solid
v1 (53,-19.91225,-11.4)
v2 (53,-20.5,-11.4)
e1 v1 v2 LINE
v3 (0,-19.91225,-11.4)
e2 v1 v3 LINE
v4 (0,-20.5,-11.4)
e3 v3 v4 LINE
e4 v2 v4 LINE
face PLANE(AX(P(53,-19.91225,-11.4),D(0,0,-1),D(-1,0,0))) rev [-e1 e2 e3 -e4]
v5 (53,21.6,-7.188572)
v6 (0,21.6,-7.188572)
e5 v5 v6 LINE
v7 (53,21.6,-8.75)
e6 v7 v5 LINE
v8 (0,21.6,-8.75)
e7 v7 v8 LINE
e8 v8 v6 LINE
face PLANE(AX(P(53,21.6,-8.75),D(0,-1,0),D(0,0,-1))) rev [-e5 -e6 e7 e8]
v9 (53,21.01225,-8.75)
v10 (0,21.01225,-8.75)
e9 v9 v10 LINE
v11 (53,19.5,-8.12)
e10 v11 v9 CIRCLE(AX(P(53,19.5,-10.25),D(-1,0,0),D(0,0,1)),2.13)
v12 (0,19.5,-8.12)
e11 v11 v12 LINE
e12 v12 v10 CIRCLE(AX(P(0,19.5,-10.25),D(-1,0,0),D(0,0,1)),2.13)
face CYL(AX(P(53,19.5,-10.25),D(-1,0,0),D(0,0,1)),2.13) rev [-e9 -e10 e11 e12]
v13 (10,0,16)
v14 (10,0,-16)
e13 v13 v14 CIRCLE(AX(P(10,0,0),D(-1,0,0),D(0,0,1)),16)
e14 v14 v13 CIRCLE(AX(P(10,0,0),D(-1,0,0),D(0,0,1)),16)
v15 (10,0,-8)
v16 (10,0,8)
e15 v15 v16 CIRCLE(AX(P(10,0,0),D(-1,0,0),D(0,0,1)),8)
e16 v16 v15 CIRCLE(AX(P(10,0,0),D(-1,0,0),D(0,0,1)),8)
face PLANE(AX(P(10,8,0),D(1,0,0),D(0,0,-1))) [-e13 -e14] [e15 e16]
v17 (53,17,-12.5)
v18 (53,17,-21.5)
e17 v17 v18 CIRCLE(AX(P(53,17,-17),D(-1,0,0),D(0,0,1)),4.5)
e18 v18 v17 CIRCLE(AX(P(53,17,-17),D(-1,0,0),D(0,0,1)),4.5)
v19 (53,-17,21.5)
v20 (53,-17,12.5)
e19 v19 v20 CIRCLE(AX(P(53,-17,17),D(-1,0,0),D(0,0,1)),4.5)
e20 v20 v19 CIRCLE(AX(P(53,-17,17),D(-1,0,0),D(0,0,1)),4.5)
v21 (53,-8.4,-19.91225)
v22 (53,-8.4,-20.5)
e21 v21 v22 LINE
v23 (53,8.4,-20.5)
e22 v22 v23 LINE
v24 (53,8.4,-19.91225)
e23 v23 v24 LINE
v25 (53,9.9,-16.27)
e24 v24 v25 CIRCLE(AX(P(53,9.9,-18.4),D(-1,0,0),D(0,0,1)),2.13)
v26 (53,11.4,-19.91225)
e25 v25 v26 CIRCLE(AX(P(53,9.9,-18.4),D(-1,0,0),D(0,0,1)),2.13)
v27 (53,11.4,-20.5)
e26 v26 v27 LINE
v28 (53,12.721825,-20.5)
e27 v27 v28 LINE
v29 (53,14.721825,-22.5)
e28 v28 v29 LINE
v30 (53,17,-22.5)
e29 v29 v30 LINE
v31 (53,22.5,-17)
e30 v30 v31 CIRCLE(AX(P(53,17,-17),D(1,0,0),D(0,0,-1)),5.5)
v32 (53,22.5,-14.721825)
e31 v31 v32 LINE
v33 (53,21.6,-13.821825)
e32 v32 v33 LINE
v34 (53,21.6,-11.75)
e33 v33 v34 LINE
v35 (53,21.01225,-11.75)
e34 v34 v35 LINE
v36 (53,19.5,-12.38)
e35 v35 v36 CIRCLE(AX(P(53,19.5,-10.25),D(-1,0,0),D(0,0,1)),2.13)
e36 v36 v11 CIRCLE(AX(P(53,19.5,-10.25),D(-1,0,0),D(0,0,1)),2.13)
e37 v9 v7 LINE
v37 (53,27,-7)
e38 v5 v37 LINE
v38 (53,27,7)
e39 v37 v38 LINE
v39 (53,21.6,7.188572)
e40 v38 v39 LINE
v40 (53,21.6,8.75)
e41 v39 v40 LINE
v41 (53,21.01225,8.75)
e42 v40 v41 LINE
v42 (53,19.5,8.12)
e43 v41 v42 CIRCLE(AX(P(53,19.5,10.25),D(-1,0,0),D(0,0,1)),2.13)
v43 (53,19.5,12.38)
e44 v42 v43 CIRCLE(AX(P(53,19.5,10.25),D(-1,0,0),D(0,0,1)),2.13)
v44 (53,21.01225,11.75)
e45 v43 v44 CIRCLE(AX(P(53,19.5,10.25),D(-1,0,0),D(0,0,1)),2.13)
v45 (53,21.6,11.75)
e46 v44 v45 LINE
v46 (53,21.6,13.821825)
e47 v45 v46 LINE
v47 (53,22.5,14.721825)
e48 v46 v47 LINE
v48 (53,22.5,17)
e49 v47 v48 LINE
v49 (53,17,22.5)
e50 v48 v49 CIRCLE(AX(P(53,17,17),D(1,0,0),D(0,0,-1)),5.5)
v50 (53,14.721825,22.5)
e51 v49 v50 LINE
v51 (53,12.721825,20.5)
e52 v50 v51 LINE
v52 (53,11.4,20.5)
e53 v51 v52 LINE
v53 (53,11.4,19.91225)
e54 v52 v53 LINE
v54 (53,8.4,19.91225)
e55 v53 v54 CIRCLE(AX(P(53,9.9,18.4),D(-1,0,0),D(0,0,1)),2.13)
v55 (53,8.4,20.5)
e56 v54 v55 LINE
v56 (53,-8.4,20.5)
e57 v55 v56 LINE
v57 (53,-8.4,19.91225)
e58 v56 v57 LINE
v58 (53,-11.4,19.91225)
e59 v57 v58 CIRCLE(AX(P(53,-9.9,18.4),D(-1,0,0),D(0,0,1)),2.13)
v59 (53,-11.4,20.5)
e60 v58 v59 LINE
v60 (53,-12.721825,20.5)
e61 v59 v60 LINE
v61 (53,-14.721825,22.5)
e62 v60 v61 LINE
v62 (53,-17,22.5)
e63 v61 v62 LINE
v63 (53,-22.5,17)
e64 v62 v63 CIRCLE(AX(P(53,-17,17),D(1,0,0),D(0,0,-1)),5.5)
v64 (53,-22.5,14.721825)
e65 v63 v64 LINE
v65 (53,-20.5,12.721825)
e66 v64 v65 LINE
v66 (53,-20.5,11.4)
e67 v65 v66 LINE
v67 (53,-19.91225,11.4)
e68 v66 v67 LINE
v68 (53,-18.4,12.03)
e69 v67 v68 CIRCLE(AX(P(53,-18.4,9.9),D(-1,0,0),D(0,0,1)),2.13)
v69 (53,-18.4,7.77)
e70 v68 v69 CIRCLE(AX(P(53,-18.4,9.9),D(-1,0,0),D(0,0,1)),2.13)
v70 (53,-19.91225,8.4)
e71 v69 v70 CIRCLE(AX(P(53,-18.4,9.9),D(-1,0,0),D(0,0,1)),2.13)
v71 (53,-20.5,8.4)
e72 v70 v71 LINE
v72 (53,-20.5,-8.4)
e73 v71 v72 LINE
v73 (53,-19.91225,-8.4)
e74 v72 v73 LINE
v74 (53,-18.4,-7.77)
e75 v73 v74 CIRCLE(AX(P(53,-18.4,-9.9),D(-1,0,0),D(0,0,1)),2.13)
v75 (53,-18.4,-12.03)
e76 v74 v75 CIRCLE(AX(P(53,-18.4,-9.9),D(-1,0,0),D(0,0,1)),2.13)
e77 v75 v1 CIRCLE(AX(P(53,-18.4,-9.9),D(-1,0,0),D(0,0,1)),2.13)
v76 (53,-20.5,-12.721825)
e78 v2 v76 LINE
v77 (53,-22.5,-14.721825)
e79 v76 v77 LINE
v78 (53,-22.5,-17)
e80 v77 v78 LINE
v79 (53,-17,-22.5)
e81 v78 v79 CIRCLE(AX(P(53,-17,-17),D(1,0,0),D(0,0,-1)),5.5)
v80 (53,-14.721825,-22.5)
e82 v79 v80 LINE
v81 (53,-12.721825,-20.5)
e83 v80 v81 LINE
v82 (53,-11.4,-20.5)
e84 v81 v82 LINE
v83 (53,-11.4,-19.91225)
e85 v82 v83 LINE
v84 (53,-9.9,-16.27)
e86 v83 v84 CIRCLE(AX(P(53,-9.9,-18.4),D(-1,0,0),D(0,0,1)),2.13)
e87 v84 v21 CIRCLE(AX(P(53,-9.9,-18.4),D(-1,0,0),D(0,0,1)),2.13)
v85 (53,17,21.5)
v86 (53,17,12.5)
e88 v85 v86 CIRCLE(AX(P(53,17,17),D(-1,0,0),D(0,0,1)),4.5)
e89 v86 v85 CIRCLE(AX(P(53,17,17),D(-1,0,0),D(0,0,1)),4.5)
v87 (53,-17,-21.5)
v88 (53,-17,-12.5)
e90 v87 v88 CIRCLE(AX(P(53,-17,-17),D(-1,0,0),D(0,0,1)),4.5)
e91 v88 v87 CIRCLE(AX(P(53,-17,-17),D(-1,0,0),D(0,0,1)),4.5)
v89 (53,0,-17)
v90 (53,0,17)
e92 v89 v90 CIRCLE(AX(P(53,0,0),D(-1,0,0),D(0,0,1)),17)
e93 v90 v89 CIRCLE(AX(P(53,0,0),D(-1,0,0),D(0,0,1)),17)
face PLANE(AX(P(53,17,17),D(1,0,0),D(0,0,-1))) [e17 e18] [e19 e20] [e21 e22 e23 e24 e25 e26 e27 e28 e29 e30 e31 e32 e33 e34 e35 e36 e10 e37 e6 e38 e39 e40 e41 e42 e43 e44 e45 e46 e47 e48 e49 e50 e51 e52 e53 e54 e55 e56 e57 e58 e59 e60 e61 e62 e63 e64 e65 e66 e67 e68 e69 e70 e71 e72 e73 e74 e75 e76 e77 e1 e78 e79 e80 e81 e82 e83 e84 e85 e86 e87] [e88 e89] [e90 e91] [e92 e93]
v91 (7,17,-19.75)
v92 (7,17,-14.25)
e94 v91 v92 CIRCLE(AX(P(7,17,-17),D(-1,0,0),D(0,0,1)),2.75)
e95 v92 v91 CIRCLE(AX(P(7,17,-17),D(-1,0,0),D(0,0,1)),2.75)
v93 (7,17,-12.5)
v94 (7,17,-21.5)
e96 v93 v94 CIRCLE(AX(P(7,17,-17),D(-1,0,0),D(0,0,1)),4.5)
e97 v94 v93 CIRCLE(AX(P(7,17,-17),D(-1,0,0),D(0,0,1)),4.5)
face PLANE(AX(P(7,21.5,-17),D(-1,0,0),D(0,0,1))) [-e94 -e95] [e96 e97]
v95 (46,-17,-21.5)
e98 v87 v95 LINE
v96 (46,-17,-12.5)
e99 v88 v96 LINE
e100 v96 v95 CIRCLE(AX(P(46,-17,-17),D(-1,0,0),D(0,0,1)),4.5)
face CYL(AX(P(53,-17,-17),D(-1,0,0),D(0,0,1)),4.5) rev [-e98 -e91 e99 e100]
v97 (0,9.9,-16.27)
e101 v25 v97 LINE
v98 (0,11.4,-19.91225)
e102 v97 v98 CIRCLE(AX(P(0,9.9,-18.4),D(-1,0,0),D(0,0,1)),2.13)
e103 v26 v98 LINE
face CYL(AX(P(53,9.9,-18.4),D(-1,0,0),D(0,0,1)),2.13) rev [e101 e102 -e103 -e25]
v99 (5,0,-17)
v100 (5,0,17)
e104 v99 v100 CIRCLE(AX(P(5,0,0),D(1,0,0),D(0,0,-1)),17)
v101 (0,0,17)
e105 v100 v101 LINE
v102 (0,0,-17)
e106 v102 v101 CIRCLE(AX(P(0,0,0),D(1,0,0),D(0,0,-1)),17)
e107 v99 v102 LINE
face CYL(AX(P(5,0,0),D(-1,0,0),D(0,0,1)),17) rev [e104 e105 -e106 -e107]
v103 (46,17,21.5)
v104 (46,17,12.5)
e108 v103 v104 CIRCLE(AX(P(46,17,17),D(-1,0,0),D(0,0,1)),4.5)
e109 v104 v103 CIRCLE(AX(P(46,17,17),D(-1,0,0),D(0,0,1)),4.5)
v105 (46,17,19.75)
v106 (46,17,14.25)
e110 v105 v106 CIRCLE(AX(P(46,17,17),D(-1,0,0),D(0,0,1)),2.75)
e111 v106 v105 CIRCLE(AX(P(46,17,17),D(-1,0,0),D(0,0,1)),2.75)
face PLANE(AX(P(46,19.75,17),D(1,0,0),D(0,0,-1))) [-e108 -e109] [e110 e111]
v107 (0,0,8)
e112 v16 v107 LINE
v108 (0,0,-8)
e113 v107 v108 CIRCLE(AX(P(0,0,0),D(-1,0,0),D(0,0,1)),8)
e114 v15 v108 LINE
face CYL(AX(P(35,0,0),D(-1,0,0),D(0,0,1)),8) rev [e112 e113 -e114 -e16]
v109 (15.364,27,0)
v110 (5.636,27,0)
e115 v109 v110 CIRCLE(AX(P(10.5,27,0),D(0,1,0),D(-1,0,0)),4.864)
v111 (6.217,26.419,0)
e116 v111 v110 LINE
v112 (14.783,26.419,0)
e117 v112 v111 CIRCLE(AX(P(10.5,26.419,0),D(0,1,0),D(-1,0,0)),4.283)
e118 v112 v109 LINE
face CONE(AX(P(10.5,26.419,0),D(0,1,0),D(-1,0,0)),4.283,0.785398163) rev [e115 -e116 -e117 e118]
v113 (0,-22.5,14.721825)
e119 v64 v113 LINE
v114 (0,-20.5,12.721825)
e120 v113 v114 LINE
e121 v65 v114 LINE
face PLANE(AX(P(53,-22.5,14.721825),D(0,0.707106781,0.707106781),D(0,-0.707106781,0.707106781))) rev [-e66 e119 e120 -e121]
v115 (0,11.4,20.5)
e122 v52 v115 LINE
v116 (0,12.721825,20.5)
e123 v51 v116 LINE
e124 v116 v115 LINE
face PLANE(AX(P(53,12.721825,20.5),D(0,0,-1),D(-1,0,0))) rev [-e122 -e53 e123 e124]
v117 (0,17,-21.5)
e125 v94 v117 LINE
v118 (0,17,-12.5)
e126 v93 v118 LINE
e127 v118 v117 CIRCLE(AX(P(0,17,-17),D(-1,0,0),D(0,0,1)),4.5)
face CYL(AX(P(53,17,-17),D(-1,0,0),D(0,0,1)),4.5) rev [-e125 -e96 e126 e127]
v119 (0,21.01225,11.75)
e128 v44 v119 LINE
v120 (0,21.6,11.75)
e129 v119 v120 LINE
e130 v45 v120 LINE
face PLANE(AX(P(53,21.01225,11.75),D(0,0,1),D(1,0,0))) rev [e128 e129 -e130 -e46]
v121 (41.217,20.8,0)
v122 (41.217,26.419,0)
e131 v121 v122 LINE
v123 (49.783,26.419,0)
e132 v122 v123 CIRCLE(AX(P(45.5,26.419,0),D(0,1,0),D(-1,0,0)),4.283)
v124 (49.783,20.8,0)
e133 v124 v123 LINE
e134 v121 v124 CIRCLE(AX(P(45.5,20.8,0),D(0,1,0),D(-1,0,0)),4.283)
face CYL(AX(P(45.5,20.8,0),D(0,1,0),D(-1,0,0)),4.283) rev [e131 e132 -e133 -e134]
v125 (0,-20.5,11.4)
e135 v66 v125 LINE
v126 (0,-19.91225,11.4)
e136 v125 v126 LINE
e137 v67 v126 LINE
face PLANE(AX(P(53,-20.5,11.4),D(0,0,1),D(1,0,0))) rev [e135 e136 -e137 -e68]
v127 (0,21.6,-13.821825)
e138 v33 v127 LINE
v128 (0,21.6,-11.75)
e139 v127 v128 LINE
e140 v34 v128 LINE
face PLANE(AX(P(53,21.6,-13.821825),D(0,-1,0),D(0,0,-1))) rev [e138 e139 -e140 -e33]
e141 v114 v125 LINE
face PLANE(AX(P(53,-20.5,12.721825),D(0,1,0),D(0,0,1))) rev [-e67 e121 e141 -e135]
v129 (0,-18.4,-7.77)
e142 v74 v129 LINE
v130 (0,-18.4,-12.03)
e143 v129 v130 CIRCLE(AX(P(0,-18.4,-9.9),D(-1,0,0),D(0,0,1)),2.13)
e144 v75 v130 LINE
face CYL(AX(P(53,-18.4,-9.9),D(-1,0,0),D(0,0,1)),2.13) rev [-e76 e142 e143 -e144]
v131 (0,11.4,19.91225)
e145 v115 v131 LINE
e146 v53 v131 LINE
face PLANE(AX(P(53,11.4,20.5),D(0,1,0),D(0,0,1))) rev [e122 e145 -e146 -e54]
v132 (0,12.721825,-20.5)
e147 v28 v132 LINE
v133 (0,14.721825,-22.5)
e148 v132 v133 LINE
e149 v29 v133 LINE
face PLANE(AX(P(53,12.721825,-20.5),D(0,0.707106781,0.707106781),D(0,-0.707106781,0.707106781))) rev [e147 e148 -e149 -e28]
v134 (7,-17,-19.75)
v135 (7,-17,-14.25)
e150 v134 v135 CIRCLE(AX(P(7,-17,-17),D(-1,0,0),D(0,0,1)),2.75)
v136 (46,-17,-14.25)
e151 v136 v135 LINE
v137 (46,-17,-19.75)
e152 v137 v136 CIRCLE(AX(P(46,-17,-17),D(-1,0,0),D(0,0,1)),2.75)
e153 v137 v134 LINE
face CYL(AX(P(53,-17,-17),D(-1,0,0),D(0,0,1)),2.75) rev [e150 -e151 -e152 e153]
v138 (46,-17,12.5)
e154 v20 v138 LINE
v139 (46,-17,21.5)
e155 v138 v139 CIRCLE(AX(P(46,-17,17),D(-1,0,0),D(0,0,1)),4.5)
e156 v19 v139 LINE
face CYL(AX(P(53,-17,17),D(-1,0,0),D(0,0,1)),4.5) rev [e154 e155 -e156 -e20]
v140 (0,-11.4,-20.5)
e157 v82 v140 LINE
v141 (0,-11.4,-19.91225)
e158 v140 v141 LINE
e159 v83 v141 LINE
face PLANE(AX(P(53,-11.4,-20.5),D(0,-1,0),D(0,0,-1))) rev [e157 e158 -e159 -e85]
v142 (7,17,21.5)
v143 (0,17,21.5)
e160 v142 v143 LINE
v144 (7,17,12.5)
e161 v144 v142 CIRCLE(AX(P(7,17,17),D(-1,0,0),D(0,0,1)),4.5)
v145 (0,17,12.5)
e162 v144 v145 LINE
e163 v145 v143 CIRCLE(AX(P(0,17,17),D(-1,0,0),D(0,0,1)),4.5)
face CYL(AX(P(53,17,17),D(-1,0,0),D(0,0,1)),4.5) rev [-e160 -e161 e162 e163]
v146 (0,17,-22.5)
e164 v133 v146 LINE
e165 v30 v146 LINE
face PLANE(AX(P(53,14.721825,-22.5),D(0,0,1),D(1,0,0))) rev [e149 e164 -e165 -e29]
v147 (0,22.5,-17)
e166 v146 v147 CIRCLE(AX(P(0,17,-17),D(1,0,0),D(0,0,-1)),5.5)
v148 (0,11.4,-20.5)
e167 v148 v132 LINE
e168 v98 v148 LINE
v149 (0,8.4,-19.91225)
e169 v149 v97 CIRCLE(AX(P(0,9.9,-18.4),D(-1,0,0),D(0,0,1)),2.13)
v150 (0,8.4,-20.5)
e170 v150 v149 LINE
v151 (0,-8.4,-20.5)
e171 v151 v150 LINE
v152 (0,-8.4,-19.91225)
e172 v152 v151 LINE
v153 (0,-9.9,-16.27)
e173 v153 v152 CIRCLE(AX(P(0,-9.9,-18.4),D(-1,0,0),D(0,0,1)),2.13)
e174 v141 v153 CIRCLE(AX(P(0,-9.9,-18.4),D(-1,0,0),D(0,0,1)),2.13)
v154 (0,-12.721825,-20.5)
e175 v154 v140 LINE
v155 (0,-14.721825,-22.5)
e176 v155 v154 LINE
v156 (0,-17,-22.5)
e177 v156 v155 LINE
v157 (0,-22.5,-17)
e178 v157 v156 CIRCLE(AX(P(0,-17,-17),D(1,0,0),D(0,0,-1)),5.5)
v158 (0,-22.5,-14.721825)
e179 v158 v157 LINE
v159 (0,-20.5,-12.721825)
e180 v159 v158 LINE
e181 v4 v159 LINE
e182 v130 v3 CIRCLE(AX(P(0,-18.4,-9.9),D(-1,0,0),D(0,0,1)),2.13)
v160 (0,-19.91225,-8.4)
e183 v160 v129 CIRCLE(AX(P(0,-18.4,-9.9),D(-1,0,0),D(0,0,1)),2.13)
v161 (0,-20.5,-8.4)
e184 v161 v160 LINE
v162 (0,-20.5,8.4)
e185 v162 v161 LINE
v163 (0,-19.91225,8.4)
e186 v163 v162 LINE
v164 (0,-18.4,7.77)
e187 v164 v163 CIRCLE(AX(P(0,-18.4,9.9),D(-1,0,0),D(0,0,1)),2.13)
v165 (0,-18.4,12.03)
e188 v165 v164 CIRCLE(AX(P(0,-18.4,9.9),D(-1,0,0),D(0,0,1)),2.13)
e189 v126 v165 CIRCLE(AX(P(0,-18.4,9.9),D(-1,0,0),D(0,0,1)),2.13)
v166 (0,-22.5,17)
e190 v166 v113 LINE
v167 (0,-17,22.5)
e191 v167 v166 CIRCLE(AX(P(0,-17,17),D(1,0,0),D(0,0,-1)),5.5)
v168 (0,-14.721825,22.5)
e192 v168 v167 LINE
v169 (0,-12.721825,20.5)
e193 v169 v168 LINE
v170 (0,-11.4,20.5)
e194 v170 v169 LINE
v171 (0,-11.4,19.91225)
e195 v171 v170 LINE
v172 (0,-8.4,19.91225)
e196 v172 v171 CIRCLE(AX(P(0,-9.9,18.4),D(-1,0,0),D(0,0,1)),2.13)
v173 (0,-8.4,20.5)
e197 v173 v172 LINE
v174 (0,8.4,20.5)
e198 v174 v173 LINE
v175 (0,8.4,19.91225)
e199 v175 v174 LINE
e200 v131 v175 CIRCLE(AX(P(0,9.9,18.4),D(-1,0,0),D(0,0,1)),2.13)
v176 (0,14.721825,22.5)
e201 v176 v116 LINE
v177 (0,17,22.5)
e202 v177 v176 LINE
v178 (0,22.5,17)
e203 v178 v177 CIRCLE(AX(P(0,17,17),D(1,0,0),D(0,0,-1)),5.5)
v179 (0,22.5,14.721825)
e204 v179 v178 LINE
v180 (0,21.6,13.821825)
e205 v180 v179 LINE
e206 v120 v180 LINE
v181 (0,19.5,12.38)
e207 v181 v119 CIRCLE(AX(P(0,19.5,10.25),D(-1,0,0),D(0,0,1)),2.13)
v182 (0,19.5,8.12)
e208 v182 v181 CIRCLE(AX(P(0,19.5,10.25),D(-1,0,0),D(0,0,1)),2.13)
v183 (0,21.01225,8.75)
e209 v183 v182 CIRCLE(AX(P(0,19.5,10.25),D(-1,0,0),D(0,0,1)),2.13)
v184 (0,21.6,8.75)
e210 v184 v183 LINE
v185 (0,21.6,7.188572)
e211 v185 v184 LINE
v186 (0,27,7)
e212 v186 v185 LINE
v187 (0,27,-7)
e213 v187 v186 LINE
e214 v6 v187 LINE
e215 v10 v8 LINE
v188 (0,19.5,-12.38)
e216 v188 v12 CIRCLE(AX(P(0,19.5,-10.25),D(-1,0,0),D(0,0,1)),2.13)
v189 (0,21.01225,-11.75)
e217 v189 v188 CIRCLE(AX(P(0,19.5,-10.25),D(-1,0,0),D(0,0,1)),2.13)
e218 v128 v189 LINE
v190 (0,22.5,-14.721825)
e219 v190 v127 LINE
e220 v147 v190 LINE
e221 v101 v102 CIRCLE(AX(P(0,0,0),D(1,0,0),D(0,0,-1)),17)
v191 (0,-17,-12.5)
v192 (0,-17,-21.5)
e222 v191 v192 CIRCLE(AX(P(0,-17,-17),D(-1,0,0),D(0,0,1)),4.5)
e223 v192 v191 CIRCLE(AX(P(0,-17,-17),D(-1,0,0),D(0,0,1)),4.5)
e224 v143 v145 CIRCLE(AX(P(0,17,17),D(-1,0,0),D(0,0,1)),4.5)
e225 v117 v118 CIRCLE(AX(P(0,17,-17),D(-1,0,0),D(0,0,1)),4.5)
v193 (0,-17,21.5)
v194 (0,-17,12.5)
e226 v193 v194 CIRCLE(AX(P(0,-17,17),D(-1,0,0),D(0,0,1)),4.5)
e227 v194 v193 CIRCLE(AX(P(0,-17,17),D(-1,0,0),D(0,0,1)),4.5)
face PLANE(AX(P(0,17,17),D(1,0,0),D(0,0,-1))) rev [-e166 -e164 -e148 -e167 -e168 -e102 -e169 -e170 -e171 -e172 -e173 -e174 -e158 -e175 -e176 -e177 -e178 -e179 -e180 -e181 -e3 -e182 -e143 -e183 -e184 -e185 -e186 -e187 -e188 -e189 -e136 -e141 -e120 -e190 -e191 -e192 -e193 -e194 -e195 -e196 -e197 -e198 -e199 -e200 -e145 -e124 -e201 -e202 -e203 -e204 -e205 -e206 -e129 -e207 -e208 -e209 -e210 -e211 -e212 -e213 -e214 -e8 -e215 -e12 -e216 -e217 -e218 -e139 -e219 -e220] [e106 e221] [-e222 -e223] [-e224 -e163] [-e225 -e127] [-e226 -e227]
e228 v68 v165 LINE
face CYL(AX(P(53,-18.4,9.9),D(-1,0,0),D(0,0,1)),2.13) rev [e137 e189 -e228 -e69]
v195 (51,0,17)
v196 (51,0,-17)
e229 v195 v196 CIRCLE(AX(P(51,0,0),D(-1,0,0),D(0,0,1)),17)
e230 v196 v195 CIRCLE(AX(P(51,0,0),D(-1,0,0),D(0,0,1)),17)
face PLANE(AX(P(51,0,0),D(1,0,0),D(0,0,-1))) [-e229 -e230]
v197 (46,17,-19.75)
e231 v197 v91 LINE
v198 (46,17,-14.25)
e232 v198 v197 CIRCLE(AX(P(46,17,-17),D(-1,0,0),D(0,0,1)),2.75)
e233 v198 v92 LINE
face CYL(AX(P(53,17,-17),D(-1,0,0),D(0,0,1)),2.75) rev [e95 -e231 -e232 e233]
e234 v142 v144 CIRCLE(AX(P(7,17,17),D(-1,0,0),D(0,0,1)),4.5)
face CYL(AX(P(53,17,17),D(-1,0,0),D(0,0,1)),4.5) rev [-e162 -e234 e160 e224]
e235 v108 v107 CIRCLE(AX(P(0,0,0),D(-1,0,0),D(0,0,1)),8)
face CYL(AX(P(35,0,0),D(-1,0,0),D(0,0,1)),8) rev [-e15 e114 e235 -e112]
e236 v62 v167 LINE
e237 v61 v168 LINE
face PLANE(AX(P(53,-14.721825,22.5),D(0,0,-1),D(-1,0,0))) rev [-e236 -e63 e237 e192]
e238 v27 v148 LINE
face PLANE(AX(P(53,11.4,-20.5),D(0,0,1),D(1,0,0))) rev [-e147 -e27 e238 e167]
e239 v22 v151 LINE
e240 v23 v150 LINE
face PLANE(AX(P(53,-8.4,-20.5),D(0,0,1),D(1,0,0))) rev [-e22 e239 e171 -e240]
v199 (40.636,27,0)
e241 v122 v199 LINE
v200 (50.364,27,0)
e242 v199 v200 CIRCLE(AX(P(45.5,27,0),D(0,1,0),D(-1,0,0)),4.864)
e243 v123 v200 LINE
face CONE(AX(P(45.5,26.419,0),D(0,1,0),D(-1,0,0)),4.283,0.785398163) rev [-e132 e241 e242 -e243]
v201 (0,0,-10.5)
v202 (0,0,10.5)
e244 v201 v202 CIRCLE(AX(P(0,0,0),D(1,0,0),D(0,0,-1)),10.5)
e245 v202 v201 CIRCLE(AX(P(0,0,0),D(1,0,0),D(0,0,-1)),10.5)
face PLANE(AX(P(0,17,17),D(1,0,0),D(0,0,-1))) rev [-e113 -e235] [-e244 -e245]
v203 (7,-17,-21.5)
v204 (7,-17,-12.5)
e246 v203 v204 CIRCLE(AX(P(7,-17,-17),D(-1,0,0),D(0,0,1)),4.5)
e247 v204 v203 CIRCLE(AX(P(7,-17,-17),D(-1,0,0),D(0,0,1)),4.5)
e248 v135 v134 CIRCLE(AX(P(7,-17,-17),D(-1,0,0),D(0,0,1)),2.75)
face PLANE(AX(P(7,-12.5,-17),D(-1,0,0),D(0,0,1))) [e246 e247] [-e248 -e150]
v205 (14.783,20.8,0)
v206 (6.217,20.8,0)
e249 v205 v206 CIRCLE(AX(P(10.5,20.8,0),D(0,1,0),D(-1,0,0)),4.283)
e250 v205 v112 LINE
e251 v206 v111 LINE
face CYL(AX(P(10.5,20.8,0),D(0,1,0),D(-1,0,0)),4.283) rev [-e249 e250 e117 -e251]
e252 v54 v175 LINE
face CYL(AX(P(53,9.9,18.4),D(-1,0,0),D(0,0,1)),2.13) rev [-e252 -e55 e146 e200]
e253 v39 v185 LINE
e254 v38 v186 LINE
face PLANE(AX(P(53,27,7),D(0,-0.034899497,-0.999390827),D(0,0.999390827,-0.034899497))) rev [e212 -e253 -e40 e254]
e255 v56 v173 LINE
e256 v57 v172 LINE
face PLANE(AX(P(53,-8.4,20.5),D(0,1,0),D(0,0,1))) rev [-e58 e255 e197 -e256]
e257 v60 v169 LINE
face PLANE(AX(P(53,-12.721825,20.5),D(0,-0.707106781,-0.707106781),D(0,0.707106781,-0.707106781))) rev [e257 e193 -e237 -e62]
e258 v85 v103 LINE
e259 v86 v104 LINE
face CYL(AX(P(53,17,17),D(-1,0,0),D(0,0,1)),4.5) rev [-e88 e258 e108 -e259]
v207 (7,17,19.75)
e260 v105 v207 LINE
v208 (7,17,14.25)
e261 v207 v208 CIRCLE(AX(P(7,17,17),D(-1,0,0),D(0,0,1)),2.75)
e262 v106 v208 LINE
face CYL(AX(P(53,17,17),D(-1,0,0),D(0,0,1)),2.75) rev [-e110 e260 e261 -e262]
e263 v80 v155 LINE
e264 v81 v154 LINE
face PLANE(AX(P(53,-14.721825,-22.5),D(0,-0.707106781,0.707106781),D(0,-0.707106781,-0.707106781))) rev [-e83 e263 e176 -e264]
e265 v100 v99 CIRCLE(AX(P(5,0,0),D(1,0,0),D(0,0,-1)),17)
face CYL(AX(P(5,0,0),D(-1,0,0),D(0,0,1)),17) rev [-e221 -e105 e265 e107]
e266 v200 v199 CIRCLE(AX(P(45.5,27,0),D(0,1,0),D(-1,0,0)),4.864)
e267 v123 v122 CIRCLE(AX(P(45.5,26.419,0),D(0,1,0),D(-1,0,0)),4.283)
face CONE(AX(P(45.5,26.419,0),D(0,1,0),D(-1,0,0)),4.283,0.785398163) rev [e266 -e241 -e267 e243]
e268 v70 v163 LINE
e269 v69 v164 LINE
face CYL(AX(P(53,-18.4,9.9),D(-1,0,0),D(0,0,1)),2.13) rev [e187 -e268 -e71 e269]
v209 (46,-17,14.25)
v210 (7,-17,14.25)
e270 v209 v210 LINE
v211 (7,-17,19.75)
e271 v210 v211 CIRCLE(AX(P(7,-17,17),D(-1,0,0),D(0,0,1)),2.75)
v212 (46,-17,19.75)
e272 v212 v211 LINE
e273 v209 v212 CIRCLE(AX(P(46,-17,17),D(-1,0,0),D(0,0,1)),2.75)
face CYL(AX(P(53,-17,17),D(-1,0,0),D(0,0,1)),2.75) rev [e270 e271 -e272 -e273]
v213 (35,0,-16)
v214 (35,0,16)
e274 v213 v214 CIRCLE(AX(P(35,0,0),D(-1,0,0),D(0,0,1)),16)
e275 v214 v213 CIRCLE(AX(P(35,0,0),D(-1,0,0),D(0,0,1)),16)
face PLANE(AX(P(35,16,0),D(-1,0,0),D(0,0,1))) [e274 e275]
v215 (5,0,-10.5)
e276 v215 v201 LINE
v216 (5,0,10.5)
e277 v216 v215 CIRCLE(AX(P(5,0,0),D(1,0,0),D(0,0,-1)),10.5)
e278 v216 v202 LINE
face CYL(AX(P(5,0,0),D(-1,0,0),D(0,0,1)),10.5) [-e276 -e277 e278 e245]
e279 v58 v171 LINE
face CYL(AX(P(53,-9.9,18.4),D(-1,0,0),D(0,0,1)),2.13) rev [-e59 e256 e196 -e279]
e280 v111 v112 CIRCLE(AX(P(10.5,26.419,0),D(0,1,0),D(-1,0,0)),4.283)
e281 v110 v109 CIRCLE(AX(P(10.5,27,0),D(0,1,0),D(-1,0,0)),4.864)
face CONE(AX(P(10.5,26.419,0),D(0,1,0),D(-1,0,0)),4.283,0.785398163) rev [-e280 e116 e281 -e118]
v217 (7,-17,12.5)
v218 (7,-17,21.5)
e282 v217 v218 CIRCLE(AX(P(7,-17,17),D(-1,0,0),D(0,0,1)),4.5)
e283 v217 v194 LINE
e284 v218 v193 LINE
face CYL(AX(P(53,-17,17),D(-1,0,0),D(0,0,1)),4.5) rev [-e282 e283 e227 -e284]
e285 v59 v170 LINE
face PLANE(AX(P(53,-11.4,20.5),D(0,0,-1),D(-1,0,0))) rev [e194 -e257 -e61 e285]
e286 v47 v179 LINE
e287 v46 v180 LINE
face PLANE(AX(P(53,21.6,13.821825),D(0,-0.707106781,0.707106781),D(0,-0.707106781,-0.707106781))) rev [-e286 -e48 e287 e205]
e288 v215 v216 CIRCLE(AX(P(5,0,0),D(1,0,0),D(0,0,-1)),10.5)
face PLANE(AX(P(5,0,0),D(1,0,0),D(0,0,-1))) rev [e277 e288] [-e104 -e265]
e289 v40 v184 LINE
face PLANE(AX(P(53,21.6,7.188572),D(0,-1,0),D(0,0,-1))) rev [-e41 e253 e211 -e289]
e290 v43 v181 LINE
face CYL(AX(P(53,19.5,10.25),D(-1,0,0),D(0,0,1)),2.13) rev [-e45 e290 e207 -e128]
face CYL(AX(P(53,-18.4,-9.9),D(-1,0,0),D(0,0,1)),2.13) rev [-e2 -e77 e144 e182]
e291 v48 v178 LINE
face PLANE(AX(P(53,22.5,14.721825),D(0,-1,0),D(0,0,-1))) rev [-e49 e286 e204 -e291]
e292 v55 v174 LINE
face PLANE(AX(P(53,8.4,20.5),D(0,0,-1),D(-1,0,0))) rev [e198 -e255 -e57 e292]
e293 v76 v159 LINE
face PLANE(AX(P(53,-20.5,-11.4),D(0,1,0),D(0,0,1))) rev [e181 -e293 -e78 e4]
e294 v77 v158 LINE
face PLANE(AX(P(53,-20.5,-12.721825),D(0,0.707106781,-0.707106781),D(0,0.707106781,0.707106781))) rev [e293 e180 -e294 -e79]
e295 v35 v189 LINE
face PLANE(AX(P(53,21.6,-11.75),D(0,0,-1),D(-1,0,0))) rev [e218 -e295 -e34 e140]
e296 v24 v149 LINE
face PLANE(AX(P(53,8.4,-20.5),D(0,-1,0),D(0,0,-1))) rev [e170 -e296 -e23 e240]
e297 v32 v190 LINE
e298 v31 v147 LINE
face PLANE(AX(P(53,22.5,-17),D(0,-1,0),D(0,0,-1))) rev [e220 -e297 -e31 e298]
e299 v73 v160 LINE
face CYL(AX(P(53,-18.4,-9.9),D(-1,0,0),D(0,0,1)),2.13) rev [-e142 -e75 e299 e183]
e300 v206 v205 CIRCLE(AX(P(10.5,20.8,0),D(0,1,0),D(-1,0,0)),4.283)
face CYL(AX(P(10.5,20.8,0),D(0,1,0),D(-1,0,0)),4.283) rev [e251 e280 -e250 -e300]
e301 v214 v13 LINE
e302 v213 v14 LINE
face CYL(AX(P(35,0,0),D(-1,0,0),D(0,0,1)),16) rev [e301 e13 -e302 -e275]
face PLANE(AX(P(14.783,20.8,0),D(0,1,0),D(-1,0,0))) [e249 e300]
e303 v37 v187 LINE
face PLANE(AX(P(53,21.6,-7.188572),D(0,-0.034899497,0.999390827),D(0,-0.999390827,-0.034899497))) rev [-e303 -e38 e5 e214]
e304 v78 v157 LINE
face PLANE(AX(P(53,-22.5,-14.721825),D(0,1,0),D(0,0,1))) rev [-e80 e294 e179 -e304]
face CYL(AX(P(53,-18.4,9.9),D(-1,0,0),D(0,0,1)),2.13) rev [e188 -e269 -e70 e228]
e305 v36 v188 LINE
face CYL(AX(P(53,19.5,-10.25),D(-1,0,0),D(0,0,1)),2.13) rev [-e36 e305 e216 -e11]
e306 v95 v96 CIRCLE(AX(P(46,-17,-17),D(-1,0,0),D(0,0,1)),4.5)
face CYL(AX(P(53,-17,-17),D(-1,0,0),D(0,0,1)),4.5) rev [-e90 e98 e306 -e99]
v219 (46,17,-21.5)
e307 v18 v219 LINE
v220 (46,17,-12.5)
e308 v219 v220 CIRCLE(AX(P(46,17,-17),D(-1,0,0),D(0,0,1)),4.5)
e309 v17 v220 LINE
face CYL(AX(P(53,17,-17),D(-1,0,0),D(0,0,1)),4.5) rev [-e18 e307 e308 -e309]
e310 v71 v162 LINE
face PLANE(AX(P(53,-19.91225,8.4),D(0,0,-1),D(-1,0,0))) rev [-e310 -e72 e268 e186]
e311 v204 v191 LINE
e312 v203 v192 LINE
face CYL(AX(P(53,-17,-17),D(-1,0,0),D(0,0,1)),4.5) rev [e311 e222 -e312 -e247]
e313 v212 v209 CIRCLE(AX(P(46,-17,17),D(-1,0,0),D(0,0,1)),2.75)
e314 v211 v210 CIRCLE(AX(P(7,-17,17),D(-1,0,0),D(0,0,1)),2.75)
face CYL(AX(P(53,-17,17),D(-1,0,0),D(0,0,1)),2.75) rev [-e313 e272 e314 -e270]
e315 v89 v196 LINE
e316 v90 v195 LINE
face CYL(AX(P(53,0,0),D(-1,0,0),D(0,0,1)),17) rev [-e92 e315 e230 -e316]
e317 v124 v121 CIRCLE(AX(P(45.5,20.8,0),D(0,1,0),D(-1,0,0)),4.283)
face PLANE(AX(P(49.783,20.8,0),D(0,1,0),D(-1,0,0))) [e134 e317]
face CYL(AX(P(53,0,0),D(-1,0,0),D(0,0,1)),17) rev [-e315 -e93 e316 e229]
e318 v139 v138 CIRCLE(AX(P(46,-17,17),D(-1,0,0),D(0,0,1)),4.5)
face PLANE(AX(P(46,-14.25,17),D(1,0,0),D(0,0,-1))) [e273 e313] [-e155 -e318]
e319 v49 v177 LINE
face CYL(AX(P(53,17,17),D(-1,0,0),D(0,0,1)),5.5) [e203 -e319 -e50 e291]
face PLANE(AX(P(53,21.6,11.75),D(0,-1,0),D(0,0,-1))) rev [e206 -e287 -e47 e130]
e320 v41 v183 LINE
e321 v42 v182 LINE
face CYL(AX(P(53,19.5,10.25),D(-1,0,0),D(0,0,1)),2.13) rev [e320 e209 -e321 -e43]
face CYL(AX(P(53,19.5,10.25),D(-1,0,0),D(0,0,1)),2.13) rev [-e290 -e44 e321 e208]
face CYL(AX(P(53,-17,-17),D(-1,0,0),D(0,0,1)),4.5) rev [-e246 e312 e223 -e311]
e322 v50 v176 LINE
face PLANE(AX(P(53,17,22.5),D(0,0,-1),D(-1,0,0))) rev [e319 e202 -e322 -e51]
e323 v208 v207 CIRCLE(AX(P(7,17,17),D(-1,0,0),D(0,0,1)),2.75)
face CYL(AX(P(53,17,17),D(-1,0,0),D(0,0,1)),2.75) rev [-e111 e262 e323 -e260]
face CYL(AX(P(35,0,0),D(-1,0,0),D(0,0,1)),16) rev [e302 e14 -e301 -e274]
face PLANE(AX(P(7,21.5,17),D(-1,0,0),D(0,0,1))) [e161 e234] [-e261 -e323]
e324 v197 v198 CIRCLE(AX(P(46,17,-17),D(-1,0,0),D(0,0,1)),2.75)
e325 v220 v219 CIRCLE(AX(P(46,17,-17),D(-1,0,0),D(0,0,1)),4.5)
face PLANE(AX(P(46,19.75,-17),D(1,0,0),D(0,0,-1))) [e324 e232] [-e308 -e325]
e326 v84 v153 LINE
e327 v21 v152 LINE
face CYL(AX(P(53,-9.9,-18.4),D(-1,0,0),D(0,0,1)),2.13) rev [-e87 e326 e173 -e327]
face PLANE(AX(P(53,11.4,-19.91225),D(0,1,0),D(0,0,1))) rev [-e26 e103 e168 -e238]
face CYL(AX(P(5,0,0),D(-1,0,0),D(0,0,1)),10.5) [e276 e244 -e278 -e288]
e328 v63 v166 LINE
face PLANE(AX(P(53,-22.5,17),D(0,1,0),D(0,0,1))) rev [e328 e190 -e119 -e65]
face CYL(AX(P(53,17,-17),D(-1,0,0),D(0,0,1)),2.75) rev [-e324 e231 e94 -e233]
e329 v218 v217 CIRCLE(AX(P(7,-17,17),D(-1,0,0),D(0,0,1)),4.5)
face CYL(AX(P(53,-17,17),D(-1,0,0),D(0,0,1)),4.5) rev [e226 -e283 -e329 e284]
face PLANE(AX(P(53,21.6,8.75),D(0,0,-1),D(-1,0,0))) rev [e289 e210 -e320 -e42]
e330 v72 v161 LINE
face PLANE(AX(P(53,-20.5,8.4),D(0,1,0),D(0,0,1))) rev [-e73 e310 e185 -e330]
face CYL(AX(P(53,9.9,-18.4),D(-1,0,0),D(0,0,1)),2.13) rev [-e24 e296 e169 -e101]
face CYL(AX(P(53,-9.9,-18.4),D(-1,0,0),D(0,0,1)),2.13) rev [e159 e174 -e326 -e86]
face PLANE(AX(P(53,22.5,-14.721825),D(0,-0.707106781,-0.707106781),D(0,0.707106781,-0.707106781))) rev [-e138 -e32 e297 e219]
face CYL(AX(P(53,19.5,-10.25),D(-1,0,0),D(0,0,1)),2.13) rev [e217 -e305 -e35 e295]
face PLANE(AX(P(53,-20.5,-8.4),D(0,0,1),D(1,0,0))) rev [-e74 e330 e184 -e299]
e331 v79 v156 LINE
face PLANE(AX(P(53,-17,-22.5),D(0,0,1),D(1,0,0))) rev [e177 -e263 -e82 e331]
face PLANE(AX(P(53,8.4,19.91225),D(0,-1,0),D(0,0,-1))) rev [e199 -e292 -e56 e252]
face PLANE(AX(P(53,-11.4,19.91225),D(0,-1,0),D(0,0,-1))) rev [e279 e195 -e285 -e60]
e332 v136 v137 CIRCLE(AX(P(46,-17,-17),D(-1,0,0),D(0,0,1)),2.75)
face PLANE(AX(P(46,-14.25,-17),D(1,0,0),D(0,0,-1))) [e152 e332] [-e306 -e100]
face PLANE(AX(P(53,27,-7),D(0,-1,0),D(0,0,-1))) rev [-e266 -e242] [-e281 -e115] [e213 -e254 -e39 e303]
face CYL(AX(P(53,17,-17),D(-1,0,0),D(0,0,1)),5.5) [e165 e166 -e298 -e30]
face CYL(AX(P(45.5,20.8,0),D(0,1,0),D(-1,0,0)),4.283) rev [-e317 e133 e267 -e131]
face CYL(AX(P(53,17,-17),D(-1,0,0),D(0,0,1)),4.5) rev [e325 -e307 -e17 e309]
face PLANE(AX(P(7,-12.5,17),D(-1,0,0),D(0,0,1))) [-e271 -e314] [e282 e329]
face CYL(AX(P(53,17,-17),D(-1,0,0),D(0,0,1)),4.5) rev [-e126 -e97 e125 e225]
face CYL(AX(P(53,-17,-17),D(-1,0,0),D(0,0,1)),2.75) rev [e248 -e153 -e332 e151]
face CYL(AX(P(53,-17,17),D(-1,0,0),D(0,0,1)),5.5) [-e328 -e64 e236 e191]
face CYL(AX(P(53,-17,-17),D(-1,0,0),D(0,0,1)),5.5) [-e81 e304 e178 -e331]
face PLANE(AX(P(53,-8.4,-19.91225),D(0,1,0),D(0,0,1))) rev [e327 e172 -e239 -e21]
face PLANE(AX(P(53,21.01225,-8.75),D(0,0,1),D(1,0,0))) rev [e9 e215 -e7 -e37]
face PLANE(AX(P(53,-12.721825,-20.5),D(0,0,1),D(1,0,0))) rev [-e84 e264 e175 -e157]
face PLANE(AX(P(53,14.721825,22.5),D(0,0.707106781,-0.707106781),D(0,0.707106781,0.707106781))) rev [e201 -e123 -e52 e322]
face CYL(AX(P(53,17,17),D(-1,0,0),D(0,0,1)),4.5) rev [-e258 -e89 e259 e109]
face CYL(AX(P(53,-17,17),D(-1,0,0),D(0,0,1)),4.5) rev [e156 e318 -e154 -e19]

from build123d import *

# Parameters (mm, degrees)
BOSS_EXTRUDE1_DEPTH  = 53
SKETCH2_W            = 2
SKETCH2_H            = 17
CUT_EXTRUDE1_START   = 5
SKETCH3_R            = 17
SKETCH3_R_2          = 10.5
CUT_EXTRUDE1_DEPTH   = 5
LPATTERN1_COUNT      = 2
LPATTERN1_PITCH      = 34
LPATTERN1_COUNT_DIR2 = 2
LPATTERN1_PITCH_DIR2 = 34


with BuildPart() as part:
    # Sketch1 → Boss-Extrude1 (new body)
    with BuildSketch(Plane(origin=(0, 0, 0), x_dir=(0, 0, -1), z_dir=(1, 0, 0))):
        with BuildLine():
            Line((-22.5, 17), (-22.5, 14.721825407))
            Line((-22.5, 14.721825407), (-20.5, 12.721825407))
            Line((-20.5, 12.721825407), (-20.5, 11.4))
            Line((-20.5, 11.4), (-19.912249979, 11.4))
            ThreePointArc((-19.912249979, 11.4), (-16.27, 9.9), (-19.912249979, 8.4))
            Line((-19.912249979, 8.4), (-20.5, 8.4))
            Line((-20.5, 8.4), (-20.5, -8.4))
            Line((-20.5, -8.4), (-19.912249979, -8.4))
            ThreePointArc((-19.912249979, -8.4), (-16.27, -9.9), (-19.912249979, -11.4))
            Line((-19.912249979, -11.4), (-20.5, -11.4))
            Line((-20.5, -11.4), (-20.5, -12.721825407))
            Line((-20.5, -12.721825407), (-22.5, -14.721825407))
            Line((-22.5, -14.721825407), (-22.5, -17))
            ThreePointArc((-22.5, -17), (-20.889087297, -20.889087297), (-17, -22.5))
            Line((-17, -22.5), (-14.721825407, -22.5))
            Line((-14.721825407, -22.5), (-12.721825407, -20.5))
            Line((-12.721825407, -20.5), (-11.4, -20.5))
            Line((-11.4, -20.5), (-11.4, -19.912249979))
            ThreePointArc((-11.4, -19.912249979), (-9.9, -16.27), (-8.4, -19.912249979))
            Line((-8.4, -19.912249979), (-8.4, -20.5))
            Line((-8.4, -20.5), (8.4, -20.5))
            Line((8.4, -20.5), (8.4, -19.912249979))
            ThreePointArc((8.4, -19.912249979), (9.9, -16.27), (11.4, -19.912249979))
            Line((11.4, -19.912249979), (11.4, -20.5))
            Line((11.4, -20.5), (12.721825407, -20.5))
            Line((12.721825407, -20.5), (14.721825407, -22.5))
            Line((14.721825407, -22.5), (17, -22.5))
            ThreePointArc((17, -22.5), (20.889087297, -20.889087297), (22.5, -17))
            Line((22.5, -17), (22.5, -14.721825407))
            Line((22.5, -14.721825407), (20.5, -12.721825407))
            Line((20.5, -12.721825407), (20.5, -11.4))
            Line((20.5, -11.4), (19.912249979, -11.4))
            ThreePointArc((19.912249979, -11.4), (16.27, -9.9), (19.912249979, -8.4))
            Line((19.912249979, -8.4), (20.5, -8.4))
            Line((20.5, -8.4), (20.5, 8.4))
            Line((20.5, 8.4), (19.912249979, 8.4))
            ThreePointArc((19.912249979, 8.4), (16.27, 9.9), (19.912249979, 11.4))
            Line((19.912249979, 11.4), (20.5, 11.4))
            Line((20.5, 11.4), (20.5, 12.721825407))
            Line((20.5, 12.721825407), (22.5, 14.721825407))
            Line((22.5, 14.721825407), (22.5, 17))
            ThreePointArc((22.5, 17), (20.889087297, 20.889087297), (17, 22.5))
            Line((17, 22.5), (14.721825407, 22.5))
            Line((14.721825407, 22.5), (13.821825407, 21.6))
            Line((13.821825407, 21.6), (11.75, 21.6))
            Line((11.75, 21.6), (11.75, 21.012249979))
            ThreePointArc((11.75, 21.012249979), (10.25, 17.37), (8.75, 21.012249979))
            Line((8.75, 21.012249979), (8.75, 21.6))
            Line((8.75, 21.6), (7.188572155, 21.6))
            Line((7.188572155, 21.6), (7, 27))
            Line((7, 27), (-7, 27))
            Line((-7, 27), (-7.188572155, 21.6))
            Line((-7.188572155, 21.6), (-8.75, 21.6))
            Line((-8.75, 21.6), (-8.75, 21.012249979))
            ThreePointArc((-8.75, 21.012249979), (-10.25, 17.37), (-11.75, 21.012249979))
            Line((-11.75, 21.012249979), (-11.75, 21.6))
            Line((-11.75, 21.6), (-13.821825407, 21.6))
            Line((-13.821825407, 21.6), (-14.721825407, 22.5))
            Line((-14.721825407, 22.5), (-17, 22.5))
            ThreePointArc((-17, 22.5), (-20.889087297, 20.889087297), (-22.5, 17))
        make_face()
    extrude(amount=BOSS_EXTRUDE1_DEPTH)

    # Sketch2 → Cut-Revolve1 (revolve, cut)
    with BuildSketch(Plane.XY, mode=Mode.PRIVATE) as cut_revolve1_sk:
        with Locations((52, 8.5)):
            Rectangle(SKETCH2_W, SKETCH2_H)
    revolve(cut_revolve1_sk.sketch.rotate(Axis((53, 0, 0), (-1, 0, 0)), 270), axis=Axis((53, 0, 0), (-1, 0, 0)), mode=Mode.SUBTRACT)

    # Sketch3 → Cut-Extrude1 (cut)
    with BuildSketch(Plane(origin=(0, 0, 0), x_dir=(0, 0, -1), z_dir=(1, 0, 0)).offset(CUT_EXTRUDE1_START)):
        with Locations(Location((0, 0, 0), (0, 0, 180))):
            Circle(SKETCH3_R)
        Circle(SKETCH3_R_2, mode=Mode.SUBTRACT)
    extrude(amount=-CUT_EXTRUDE1_DEPTH, mode=Mode.SUBTRACT)

    # Sketch4 → Cut-Revolve2 (revolve, cut)
    with BuildSketch(Plane.XY, mode=Mode.PRIVATE) as cut_revolve2_sk:
        Polygon((0, 0), (0, 8), (10, 8), (10, 16), (35, 16), (35, 0), align=None)
    revolve(cut_revolve2_sk.sketch.rotate(Axis((35, 0, 0), (-1, 0, 0)), 270), axis=Axis((35, 0, 0), (-1, 0, 0)), mode=Mode.SUBTRACT)

    # Sketch5 → Cut-Revolve3 (revolve, cut)
    with BuildSketch(Plane.XY, mode=Mode.PRIVATE) as cut_revolve3_sk:
        Polygon((10.5, 27), (15.364, 27), (14.783, 26.419), (14.783, 20.8), (10.5, 20.8), align=None)
    revolve(cut_revolve3_sk.sketch.rotate(Axis((10.5, 20.8, 0), (0, 1, 0)), 180), axis=Axis((10.5, 20.8, 0), (0, 1, 0)), mode=Mode.SUBTRACT)

    # Sketch6 → Cut-Revolve4 (revolve, cut)
    with BuildSketch(Plane.XY, mode=Mode.PRIVATE) as cut_revolve4_sk:
        Polygon((45.5, 27), (50.364, 27), (49.783, 26.419), (49.783, 20.8), (45.5, 20.8), align=None)
    revolve(cut_revolve4_sk.sketch.rotate(Axis((45.5, 20.8, 0), (0, 1, 0)), 180), axis=Axis((45.5, 20.8, 0), (0, 1, 0)), mode=Mode.SUBTRACT)

    # Sketch7 → Cut-Revolve5 (revolve, cut)
    with BuildSketch(Plane.XY.offset(17), mode=Mode.PRIVATE) as cut_revolve5_sk:
        Polygon((0, 17), (0, 21.5), (7, 21.5), (7, 19.75), (46, 19.75), (46, 21.5), (53, 21.5), (53, 17), align=None)
    cut_revolve5 = revolve(cut_revolve5_sk.sketch.rotate(Axis((53, 17, 17), (-1, 0, 0)), 270), axis=Axis((53, 17, 17), (-1, 0, 0)), mode=Mode.SUBTRACT)

    # LPattern1: Cut-Revolve5 2 × 2
    with Locations(*[(0, -j * LPATTERN1_PITCH_DIR2, -i * LPATTERN1_PITCH) for i in range(LPATTERN1_COUNT) for j in range(LPATTERN1_COUNT_DIR2) if (i, j) != (0, 0)]):
        add(cut_revolve5, mode=Mode.SUBTRACT)


solid = part.part
